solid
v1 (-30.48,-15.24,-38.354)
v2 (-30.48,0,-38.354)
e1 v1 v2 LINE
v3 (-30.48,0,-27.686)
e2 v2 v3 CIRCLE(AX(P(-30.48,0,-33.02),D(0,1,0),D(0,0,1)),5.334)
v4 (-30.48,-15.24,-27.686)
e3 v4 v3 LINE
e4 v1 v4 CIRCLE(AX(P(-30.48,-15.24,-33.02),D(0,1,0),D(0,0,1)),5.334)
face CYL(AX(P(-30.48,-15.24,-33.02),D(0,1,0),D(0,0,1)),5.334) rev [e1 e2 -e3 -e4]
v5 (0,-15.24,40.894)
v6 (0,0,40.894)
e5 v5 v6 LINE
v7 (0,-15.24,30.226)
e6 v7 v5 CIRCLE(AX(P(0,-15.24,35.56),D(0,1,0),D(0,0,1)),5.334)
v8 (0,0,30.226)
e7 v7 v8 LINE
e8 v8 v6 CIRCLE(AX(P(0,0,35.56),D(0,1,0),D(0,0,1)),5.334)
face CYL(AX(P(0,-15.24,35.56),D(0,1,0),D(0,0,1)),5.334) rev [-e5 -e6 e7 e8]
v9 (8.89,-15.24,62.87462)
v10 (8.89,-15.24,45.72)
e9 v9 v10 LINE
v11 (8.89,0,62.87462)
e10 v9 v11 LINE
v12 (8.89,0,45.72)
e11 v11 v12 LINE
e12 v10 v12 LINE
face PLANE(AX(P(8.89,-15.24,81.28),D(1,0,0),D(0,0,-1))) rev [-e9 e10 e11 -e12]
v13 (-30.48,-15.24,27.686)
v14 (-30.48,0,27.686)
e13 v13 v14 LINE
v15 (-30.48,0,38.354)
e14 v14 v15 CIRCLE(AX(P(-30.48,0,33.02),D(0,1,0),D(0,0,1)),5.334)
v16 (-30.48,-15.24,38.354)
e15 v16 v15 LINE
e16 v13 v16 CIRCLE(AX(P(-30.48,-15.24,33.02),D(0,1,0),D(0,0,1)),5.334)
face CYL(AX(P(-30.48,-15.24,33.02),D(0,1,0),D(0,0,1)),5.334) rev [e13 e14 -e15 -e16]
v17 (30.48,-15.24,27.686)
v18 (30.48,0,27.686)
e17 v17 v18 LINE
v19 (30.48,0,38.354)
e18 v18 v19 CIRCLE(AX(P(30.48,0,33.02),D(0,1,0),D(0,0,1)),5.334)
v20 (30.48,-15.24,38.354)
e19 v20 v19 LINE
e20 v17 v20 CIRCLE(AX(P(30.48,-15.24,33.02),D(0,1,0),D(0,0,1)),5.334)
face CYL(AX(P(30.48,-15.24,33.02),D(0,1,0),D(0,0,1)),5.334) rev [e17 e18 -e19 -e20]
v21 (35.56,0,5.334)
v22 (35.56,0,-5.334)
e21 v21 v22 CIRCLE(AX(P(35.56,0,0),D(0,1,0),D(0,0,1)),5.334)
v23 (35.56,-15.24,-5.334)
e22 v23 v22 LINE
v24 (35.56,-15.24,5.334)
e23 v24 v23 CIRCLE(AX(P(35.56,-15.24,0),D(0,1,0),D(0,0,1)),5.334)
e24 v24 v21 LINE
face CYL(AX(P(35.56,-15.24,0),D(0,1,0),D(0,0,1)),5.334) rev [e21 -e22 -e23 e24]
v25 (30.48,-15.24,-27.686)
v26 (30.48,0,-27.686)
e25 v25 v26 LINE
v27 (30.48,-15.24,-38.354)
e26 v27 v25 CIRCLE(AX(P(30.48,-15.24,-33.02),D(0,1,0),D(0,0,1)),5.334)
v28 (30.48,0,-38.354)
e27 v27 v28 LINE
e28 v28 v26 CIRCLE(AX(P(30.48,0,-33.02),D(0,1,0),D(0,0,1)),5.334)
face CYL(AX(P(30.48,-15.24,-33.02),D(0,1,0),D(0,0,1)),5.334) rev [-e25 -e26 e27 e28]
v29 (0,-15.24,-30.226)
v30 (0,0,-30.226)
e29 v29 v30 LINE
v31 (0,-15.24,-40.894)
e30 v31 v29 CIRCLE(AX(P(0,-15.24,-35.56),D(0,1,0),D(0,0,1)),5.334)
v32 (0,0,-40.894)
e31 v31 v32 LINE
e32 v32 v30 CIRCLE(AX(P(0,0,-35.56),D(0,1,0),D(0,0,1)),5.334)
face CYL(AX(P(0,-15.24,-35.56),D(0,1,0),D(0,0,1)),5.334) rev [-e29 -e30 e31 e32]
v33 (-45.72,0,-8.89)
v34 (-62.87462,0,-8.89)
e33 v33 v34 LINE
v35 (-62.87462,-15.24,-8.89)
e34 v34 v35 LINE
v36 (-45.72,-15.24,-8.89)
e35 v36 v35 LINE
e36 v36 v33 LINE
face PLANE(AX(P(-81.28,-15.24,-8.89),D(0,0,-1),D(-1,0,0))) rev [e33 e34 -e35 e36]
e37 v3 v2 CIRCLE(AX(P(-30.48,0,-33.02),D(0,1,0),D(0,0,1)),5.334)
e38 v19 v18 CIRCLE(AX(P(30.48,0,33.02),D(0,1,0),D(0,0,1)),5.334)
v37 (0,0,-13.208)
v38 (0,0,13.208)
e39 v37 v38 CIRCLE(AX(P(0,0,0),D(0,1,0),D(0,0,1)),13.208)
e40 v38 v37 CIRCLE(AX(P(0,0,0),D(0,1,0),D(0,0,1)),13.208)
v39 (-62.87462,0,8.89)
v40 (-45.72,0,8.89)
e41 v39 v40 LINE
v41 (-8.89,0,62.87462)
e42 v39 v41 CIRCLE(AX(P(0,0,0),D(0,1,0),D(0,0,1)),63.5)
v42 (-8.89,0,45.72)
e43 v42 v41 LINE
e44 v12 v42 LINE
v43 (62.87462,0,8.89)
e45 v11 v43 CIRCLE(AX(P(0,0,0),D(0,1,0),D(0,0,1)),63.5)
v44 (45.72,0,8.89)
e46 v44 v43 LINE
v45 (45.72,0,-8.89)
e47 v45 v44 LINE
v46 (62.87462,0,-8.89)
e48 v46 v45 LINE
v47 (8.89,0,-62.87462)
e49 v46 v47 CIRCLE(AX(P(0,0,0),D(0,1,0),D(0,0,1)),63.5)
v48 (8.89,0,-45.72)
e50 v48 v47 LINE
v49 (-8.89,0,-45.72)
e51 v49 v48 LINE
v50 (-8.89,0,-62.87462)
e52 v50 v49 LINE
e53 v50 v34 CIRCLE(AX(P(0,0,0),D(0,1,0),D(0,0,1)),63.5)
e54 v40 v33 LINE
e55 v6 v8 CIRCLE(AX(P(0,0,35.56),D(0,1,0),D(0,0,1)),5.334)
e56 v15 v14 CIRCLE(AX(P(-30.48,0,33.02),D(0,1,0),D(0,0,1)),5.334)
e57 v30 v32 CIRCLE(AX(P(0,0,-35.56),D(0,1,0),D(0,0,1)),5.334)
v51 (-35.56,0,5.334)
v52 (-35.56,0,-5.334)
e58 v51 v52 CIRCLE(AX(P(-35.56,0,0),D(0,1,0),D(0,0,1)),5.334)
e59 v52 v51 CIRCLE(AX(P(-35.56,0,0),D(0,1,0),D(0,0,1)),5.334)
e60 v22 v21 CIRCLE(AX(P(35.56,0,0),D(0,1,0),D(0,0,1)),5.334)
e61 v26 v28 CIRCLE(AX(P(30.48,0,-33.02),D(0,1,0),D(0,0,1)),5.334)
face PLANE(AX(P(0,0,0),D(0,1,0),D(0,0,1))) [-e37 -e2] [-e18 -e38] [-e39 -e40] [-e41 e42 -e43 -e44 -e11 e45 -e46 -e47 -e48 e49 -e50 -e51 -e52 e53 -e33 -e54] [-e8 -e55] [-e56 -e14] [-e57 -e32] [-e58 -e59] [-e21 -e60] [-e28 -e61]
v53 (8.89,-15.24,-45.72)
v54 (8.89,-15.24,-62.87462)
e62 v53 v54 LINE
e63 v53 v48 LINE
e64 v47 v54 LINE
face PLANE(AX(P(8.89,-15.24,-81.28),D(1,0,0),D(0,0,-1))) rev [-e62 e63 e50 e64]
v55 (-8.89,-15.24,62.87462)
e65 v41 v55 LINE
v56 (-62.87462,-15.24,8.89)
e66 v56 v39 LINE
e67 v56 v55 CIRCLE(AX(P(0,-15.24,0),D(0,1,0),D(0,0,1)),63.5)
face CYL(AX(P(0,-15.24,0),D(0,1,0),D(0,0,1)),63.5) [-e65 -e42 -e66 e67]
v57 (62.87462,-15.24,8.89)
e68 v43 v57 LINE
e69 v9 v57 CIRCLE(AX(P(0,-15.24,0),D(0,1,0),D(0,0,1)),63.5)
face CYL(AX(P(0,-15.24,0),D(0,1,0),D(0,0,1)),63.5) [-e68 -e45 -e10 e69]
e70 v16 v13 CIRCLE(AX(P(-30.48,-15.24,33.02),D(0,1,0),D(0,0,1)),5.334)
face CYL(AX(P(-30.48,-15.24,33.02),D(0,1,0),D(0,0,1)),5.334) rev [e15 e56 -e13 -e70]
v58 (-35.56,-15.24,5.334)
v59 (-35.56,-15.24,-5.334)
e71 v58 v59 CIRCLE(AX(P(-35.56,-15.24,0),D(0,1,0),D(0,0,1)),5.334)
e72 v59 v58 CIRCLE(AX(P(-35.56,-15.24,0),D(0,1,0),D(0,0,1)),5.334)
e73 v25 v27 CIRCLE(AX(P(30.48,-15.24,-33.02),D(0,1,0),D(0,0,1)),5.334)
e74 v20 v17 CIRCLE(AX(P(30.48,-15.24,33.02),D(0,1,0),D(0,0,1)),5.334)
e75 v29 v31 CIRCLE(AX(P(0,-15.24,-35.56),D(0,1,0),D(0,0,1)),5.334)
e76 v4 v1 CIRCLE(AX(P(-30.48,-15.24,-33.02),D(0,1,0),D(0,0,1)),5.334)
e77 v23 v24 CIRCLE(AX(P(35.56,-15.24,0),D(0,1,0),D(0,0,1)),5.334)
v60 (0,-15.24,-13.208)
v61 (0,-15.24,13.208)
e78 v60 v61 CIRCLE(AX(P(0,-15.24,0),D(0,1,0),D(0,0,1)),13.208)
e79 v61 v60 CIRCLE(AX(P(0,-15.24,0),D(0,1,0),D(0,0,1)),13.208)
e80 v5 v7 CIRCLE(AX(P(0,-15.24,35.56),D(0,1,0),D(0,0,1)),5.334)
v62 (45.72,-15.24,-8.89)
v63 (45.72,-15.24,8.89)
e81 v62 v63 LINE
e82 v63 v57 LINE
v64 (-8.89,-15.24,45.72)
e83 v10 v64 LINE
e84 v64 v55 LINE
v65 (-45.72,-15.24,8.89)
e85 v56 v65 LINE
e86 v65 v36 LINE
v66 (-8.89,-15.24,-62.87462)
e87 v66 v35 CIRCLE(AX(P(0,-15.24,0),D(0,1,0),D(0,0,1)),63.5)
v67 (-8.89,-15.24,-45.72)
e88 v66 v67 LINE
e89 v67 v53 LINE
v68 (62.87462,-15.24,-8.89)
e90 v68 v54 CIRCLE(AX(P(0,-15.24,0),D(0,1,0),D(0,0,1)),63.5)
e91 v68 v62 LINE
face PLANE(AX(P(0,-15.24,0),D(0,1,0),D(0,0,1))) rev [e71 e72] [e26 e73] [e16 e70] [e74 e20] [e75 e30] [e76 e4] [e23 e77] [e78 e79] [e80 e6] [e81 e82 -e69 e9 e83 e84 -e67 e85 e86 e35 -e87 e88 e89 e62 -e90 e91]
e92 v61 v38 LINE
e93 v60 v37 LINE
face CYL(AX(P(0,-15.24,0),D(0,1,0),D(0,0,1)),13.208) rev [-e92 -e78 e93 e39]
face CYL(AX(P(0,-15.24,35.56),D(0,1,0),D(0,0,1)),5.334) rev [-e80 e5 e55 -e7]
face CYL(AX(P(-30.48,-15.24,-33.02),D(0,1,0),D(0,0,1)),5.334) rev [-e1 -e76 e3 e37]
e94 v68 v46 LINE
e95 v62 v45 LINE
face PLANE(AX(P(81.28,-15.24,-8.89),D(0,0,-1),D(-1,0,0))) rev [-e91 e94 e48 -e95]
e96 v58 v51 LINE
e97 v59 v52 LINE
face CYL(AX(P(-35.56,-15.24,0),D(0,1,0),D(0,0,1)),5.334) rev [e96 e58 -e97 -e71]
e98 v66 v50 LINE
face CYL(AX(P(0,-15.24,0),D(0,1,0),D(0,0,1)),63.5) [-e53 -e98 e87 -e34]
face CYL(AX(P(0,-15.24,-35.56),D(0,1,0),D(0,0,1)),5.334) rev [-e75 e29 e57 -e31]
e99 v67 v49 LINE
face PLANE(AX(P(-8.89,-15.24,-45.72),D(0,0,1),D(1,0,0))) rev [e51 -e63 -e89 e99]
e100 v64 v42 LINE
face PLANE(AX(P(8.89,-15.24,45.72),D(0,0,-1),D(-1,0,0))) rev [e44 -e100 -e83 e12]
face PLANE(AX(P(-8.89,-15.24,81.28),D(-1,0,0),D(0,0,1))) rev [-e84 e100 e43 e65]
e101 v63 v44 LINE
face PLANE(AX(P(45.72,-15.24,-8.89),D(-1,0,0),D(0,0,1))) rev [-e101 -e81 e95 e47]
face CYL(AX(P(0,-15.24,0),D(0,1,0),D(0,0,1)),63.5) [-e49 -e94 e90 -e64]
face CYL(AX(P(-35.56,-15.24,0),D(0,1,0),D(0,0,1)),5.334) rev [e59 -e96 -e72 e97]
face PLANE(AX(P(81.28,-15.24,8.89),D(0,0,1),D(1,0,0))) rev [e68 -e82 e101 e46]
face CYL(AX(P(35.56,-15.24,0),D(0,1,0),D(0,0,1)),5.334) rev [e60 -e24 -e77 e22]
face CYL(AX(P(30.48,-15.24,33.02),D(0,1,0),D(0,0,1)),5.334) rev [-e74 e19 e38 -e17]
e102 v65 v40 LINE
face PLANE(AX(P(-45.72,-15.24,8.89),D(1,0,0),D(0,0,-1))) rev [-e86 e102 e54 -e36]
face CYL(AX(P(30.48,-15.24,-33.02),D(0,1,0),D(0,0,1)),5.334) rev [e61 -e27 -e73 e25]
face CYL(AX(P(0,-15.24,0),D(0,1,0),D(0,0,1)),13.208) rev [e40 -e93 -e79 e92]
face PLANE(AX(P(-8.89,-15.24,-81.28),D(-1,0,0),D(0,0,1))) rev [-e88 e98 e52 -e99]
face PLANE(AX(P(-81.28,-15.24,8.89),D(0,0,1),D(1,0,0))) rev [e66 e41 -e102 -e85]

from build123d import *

# Parameters (mm, degrees)
SKETCH1_R           = 31.75
SKETCH1_R_2         = 2.667
BOSS_EXTRUDE1_DEPTH = 7.62
SKETCH2_R           = 6.604
SKETCH2_W           = 8.89
SKETCH2_H           = 17.78
CUT_EXTRUDE1_DEPTH  = 46.543269536
SKETCH3_R           = 2.667
CUT_EXTRUDE2_DEPTH  = 46.543269536
CIRPATTERN1_COUNT   = 4
SCALE1_SCALE        = 2


with BuildPart() as part:
    # Sketch1 → Boss-Extrude1 (new body)
    with BuildSketch(Plane(origin=(0, 0, 0), x_dir=(1, 0, 0), z_dir=(0, 1, 0))):
        with Locations(Location((0, 0, 0), (0, 0, 270))):
            Circle(SKETCH1_R)
        with Locations(Location((-15.24, 16.51, 0), (0, 0, 270))):
            Circle(SKETCH1_R_2, mode=Mode.SUBTRACT)
        with Locations(Location((15.24, 16.51, 0), (0, 0, 270))):
            Circle(SKETCH1_R_2, mode=Mode.SUBTRACT)
        with Locations(Location((15.24, -16.51, 0), (0, 0, 270))):
            Circle(SKETCH1_R_2, mode=Mode.SUBTRACT)
        with Locations(Location((-15.24, -16.51, 0), (0, 0, 270))):
            Circle(SKETCH1_R_2, mode=Mode.SUBTRACT)
    extrude(amount=-BOSS_EXTRUDE1_DEPTH)

    # Sketch2 → Cut-Extrude1 (cut, through all)
    with BuildSketch(Plane(origin=(0, 0, 0), x_dir=(1, 0, 0), z_dir=(0, 1, 0))):
        with Locations(Location((0, 0, 0), (0, 0, 270))):
            Circle(SKETCH2_R)
        with Locations((0, 31.75)):
            Rectangle(SKETCH2_W, SKETCH2_H)
    cut_extrude1 = extrude(amount=-CUT_EXTRUDE1_DEPTH, mode=Mode.SUBTRACT)

    # Sketch3 → Cut-Extrude2 (cut, through all)
    with BuildSketch(Plane(origin=(0, 0, 0), x_dir=(1, 0, 0), z_dir=(0, 1, 0))):
        with Locations(Location((-17.78, 0, 0), (0, 0, 270))):
            Circle(SKETCH3_R)
        with Locations(Location((0, 17.78, 0), (0, 0, 270))):
            Circle(SKETCH3_R)
        with Locations(Location((17.78, 0, 0), (0, 0, 270))):
            Circle(SKETCH3_R)
        with Locations(Location((0, -17.78, 0), (0, 0, 270))):
            Circle(SKETCH3_R)
    extrude(amount=-CUT_EXTRUDE2_DEPTH, mode=Mode.SUBTRACT)

    # CirPattern1: Cut-Extrude1 ×4 about axis
    cirpattern1_axis = Axis((0, 0, 0), (0, 1, 0))
    for i in range(1, CIRPATTERN1_COUNT):
        add(cut_extrude1.rotate(cirpattern1_axis, i * 360 / CIRPATTERN1_COUNT), mode=Mode.SUBTRACT)


with BuildPart() as part_1:
    # Scale1: scaled about (0, 0, 0)
    add(part.part.scale(SCALE1_SCALE))


solid = part_1.part
